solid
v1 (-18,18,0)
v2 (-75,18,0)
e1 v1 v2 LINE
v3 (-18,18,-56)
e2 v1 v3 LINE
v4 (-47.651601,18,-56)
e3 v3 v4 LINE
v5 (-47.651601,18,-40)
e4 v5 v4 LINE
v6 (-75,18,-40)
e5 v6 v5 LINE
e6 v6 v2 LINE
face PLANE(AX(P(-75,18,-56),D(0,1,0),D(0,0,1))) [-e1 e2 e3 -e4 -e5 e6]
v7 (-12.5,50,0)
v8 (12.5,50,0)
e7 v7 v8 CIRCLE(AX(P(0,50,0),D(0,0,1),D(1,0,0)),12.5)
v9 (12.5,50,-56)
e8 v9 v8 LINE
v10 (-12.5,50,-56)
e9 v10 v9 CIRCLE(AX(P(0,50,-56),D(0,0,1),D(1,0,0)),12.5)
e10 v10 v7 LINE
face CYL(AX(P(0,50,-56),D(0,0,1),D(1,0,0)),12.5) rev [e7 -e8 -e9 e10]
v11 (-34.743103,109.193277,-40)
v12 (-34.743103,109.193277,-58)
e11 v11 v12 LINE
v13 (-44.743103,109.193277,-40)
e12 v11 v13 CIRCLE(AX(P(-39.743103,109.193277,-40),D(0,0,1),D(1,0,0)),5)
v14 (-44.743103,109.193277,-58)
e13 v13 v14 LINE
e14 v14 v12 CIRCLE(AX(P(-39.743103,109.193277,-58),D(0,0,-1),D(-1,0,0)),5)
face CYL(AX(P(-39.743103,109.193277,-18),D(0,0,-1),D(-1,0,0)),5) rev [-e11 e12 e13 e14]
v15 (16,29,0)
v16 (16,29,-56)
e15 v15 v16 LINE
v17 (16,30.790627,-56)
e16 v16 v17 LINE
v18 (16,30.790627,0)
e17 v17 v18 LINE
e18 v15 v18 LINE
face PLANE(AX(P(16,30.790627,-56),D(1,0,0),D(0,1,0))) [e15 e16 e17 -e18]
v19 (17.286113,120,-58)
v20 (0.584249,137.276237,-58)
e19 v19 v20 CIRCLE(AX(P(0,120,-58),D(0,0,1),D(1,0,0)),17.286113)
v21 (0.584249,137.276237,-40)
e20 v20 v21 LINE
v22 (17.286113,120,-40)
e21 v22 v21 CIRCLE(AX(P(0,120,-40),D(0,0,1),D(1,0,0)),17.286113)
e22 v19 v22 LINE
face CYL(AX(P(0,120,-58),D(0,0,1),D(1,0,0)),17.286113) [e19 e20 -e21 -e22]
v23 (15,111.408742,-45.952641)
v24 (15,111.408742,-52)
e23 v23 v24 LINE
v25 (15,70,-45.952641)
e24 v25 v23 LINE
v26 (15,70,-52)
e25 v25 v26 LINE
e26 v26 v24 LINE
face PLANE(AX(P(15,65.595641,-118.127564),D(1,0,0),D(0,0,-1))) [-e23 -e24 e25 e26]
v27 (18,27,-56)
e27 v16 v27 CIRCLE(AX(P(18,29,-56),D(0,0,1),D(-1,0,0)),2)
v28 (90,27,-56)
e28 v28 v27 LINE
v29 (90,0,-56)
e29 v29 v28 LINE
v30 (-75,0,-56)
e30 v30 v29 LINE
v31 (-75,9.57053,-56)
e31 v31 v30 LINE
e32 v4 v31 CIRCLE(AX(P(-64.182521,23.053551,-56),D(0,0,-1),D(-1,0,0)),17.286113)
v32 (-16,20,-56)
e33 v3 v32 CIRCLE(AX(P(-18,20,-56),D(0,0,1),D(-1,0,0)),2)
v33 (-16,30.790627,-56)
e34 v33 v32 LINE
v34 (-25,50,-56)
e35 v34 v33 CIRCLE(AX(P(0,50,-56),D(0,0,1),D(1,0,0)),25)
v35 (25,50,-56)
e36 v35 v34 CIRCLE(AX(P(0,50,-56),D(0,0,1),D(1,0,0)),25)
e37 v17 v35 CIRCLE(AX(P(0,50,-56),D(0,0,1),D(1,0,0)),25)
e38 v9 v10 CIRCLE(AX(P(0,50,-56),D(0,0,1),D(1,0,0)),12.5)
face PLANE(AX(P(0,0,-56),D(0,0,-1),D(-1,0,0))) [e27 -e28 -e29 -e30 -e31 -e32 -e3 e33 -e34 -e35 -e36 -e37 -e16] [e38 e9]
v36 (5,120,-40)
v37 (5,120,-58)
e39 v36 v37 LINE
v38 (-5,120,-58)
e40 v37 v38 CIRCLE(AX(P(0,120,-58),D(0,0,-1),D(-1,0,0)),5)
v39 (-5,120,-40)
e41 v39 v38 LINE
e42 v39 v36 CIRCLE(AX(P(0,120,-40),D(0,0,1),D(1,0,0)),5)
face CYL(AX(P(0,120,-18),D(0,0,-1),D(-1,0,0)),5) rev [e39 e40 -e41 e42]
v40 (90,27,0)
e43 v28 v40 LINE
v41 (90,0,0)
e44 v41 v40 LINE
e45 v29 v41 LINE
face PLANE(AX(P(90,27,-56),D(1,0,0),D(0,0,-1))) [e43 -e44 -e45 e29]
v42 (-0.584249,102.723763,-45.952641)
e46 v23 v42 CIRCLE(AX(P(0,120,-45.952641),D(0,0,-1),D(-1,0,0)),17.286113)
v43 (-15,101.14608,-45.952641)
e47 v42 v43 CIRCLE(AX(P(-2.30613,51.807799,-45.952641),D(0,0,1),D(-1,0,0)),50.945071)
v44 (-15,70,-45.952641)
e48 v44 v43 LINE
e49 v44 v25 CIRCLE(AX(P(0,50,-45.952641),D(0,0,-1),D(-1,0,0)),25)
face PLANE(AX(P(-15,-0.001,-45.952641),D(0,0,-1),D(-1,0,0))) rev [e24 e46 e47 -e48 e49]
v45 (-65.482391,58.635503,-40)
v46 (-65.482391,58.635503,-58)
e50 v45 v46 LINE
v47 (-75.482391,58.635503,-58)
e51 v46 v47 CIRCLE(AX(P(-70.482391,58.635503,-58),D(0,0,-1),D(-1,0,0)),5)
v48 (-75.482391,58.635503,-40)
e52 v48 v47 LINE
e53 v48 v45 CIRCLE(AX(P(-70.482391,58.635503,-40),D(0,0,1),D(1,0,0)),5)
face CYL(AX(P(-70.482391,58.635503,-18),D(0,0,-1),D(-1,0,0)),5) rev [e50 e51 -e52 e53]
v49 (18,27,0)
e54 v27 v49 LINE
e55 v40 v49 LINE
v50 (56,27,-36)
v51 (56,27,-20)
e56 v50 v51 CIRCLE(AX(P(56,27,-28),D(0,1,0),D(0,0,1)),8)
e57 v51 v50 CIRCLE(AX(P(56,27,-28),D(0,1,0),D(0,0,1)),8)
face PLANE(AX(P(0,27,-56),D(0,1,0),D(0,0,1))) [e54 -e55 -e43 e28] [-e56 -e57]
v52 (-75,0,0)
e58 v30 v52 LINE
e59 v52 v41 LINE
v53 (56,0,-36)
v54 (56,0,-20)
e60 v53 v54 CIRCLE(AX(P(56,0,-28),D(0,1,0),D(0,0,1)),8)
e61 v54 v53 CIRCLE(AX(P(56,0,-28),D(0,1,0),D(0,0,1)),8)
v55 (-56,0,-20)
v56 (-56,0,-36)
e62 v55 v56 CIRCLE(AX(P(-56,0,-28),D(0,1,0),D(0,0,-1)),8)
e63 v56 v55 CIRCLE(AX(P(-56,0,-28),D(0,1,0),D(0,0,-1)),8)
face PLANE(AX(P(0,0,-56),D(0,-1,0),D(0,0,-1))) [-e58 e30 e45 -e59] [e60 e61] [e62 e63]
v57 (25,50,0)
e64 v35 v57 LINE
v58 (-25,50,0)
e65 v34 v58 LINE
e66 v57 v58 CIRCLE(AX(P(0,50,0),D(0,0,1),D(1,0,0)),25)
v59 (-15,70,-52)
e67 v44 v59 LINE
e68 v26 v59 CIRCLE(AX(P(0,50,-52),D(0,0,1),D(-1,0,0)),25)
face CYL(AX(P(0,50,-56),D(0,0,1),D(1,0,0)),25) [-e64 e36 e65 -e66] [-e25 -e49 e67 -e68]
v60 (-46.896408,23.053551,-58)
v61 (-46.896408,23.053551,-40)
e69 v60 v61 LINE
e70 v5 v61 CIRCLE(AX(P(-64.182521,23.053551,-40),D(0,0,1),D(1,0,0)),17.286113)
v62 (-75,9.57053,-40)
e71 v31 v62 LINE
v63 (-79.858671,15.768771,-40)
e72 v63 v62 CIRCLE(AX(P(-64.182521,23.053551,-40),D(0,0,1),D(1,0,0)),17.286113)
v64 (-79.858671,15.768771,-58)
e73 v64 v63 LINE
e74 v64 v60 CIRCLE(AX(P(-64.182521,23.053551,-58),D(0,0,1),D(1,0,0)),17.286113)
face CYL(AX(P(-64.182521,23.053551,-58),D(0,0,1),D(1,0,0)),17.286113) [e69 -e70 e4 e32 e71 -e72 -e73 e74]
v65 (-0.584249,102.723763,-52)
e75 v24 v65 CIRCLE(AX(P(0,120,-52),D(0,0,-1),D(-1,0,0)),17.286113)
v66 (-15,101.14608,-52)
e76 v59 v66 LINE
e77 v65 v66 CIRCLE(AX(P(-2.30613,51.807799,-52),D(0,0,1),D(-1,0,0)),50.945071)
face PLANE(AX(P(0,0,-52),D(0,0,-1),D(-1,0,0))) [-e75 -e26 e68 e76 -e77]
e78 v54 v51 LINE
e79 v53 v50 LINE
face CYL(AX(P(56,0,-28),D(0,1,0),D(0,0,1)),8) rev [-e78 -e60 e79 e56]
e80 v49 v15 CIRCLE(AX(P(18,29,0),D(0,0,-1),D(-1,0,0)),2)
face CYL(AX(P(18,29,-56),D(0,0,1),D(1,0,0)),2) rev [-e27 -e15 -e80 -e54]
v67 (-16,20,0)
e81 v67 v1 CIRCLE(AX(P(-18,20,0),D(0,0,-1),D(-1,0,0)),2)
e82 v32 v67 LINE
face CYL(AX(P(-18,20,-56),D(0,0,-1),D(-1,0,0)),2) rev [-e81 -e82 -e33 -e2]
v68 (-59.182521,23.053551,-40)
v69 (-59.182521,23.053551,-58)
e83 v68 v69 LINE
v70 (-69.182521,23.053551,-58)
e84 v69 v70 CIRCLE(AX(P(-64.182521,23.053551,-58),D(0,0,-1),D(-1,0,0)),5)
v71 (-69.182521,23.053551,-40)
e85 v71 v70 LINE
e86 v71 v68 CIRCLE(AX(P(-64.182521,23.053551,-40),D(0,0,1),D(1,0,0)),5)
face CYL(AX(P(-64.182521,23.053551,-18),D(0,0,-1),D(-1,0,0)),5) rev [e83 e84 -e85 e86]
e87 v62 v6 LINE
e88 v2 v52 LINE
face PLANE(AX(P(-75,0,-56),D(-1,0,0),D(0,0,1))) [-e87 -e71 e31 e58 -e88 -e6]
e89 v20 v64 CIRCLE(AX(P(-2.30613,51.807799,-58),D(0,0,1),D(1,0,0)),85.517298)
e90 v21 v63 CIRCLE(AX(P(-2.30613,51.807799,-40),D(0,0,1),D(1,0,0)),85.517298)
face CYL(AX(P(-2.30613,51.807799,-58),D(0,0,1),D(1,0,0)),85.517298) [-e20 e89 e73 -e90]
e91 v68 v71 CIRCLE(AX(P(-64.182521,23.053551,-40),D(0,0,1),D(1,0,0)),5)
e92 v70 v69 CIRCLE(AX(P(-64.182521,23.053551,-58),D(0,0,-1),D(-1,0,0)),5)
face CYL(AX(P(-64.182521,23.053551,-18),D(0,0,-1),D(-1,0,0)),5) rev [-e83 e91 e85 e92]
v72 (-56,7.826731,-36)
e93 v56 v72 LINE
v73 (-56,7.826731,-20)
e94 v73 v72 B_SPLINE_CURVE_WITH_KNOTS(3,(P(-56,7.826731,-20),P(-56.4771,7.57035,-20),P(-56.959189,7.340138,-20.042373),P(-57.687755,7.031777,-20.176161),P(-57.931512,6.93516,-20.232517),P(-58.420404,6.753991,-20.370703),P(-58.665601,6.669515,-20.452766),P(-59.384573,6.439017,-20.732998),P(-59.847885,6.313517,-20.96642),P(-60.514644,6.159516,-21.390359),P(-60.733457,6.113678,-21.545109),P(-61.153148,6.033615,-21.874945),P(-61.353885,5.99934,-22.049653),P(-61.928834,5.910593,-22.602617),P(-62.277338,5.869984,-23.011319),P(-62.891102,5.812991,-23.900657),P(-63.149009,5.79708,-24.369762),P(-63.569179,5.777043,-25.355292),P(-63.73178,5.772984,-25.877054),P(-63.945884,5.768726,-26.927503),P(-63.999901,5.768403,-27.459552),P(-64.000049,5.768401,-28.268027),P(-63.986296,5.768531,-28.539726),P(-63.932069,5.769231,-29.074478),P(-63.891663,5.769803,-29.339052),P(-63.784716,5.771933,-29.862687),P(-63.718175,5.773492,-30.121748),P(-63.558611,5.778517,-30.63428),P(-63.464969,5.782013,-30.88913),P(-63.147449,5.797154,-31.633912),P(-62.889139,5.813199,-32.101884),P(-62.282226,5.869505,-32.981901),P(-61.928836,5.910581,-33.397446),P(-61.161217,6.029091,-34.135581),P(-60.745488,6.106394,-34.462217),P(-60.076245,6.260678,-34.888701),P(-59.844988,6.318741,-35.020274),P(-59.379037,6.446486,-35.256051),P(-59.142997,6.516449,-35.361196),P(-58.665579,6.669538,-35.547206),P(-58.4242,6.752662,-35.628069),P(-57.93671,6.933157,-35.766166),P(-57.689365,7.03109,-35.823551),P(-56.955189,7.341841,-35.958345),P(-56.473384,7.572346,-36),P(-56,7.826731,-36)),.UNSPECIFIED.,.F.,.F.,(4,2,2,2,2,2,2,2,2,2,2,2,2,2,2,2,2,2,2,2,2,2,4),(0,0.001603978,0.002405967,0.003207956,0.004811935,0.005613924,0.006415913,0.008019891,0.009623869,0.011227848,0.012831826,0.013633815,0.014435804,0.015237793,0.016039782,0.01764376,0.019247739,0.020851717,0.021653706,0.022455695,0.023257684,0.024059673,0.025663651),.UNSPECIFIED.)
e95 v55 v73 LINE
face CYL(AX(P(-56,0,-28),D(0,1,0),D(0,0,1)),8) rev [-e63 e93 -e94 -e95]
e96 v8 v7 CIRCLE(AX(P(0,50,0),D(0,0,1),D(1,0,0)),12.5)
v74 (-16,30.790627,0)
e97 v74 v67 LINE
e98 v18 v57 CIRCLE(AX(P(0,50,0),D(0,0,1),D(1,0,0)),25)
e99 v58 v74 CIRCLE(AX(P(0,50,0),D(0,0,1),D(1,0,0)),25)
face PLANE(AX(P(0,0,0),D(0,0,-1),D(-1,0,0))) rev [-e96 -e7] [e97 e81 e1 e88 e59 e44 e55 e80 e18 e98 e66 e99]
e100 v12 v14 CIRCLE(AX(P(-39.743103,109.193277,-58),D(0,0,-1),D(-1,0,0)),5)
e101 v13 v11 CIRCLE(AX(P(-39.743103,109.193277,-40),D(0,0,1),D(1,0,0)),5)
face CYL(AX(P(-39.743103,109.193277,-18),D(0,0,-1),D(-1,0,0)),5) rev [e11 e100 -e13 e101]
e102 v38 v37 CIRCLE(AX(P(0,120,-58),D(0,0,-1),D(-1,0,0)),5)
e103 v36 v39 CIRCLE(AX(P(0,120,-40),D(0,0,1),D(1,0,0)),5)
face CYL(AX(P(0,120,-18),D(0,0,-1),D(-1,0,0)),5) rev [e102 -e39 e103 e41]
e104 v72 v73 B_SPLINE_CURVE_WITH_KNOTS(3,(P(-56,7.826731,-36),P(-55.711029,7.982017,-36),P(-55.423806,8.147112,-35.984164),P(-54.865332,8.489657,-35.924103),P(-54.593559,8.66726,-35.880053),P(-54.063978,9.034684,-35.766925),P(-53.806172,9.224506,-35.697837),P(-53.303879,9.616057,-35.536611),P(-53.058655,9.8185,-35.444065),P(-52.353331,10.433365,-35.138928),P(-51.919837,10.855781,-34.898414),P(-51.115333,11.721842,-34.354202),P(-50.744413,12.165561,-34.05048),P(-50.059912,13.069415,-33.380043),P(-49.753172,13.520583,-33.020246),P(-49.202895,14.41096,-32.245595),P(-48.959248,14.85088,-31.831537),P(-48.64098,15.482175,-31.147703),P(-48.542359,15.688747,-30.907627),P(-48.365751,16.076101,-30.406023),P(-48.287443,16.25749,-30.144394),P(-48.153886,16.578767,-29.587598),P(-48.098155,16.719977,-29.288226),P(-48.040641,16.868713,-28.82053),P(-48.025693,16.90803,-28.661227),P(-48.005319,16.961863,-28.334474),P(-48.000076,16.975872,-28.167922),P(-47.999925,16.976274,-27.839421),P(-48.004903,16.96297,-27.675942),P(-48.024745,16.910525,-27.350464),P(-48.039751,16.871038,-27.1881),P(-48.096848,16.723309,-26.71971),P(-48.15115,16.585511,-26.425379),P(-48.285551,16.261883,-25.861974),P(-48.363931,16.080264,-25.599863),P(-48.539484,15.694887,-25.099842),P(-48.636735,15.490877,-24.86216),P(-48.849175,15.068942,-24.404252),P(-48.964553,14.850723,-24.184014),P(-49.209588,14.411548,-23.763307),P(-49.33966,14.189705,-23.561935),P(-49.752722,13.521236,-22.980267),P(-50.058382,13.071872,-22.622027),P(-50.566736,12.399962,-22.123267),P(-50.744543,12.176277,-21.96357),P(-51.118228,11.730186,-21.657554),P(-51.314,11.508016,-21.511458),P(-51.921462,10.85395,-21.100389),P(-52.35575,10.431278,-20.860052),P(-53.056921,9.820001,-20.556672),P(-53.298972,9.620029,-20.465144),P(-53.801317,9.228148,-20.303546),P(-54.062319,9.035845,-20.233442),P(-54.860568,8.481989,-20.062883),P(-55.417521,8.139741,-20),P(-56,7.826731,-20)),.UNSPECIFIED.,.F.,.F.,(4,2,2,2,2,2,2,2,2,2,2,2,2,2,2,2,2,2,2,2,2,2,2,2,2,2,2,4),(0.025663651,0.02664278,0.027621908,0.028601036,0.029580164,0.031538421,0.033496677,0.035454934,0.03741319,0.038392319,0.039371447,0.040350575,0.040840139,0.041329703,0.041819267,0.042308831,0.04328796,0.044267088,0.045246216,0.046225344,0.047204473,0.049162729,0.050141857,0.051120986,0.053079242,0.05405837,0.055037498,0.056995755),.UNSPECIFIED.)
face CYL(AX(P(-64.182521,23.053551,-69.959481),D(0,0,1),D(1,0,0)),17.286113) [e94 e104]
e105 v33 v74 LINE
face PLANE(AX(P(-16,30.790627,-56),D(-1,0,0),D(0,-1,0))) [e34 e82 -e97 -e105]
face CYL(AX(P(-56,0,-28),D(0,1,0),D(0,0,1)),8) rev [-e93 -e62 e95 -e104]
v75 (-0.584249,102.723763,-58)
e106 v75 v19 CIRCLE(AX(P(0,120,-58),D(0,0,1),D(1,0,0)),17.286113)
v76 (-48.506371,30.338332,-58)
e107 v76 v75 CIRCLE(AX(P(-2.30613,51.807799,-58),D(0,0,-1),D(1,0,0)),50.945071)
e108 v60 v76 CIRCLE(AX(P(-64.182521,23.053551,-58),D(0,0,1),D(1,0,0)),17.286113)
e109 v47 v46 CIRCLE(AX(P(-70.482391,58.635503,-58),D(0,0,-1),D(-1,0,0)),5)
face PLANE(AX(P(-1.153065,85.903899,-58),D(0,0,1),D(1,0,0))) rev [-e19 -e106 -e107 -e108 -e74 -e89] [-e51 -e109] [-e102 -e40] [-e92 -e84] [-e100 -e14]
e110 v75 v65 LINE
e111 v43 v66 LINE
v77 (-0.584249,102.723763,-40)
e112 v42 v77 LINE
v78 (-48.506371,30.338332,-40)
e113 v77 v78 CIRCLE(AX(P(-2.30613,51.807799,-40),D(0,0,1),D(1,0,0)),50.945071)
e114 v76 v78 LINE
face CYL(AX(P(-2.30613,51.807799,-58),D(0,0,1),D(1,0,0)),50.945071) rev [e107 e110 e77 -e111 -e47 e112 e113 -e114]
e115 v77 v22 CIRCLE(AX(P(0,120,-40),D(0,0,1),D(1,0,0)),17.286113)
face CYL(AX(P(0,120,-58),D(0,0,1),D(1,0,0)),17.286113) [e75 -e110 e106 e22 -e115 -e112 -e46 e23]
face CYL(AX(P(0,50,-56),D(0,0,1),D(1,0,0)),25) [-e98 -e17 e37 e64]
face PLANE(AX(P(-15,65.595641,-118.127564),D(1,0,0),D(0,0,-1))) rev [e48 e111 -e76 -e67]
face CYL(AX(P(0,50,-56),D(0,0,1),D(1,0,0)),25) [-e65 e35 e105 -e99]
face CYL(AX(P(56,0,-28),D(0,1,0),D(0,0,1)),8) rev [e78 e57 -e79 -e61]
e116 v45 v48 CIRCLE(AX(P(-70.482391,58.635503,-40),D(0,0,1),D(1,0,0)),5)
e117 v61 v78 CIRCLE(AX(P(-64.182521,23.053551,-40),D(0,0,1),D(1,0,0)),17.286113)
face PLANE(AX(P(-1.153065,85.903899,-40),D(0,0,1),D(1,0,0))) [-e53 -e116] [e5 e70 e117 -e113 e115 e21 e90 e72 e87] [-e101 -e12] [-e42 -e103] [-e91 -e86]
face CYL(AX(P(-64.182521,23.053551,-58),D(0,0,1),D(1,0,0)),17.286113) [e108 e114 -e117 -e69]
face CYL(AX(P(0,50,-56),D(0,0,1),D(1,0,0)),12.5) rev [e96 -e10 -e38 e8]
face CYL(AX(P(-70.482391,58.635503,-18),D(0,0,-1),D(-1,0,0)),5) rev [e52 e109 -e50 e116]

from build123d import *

# Parameters (mm, degrees)
BASE_PLATE_DEPTH            = 56
HUB_BOSS_SKETCH_R           = 12.5
HUB_BOSS_DEPTH              = 56
HUB_FILLET_R2_R             = 2
WEB_SKETCH_W                = 30
WEB_SKETCH_H                = 54.40435867
WEB_4MM_DEPTH               = 52
HUB_BORE_REACH              = 162.112
HUB_BORE_END_RADIUS         = 25
HUB_BORE_SKETCH_W           = 30
HUB_BORE_SKETCH_H           = 45.952641166
FLANGE_PLATE_DEPTH          = 58
FLANGE_SLOT_CUT_DEPTH       = 40
FLANGE_BOLT_HOLES_SKETCH_R  = 5
FLANGE_BOLT_HOLES_DEPTH     = 40
BASE_MOUNTING_HOLE_SKETCH_R = 8
BASE_MOUNTING_HOLE_DEPTH    = 154.738826956
FLANGE_CLOSING_BOSS_DEPTH   = 40


with BuildPart() as part:
    # Base Plate Sketch → Base Plate (new body)
    with BuildSketch(Plane.XY):
        Polygon((0, 0), (-75, 0), (-75, 18), (0, 18), (0, 27), (90, 27), (90, 0), align=None)
    extrude(amount=-BASE_PLATE_DEPTH)

    # Hub Boss Sketch → Hub Boss (add)
    with BuildSketch(Plane.XY):
        with BuildLine():
            Line((-16, 30.790627288), (-16, 18))
            Line((-16, 18), (16, 18))
            Line((16, 18), (16, 30.790627288))
            ThreePointArc((16, 30.790627288), (0, 75), (-16, 30.790627288))
        make_face()
        with Locations((0, 50)):
            Circle(HUB_BOSS_SKETCH_R, mode=Mode.SUBTRACT)
    extrude(amount=-HUB_BOSS_DEPTH)

    # Hub Fillet R2
    hub_fillet_r2_edges = [part.edges().sort_by_distance(p)[0] for p in [
        (16, 27, -28),
        (-16, 18, -28),
    ]]
    fillet(hub_fillet_r2_edges, radius=HUB_FILLET_R2_R)

    # Web Sketch → Web 4mm (add)
    with BuildSketch(Plane.XY):
        with Locations((0, 92.797820665)):
            Rectangle(WEB_SKETCH_W, WEB_SKETCH_H)
    extrude(amount=-WEB_4MM_DEPTH)

    # Hub Bore: up to this cylinder (the profile starts outside it)
    hub_bore_end = Plane(origin=(0, 50, -22.976321), z_dir=(0, 0, 1)) * Cylinder(HUB_BORE_END_RADIUS, 375.224, mode=Mode.PRIVATE)
    # Hub Bore Sketch → Hub Bore (cut, up to the surface)
    with BuildSketch(Plane(origin=(0, 120, 0), x_dir=(1, 0, 0), z_dir=(0, 1, 0)), mode=Mode.PRIVATE) as hub_bore_sk1:
        with Locations((0, 22.976320583)):
            Rectangle(HUB_BORE_SKETCH_W, HUB_BORE_SKETCH_H)
    hub_bore_tool1 = extrude(hub_bore_sk1.sketch, amount=-HUB_BORE_REACH, mode=Mode.PRIVATE) - hub_bore_end
    add(hub_bore_tool1.solids().sort_by_distance((0, 120, -22.976321))[0], mode=Mode.SUBTRACT)

    # Flange Profile Sketch → Flange Plate (add)
    with BuildSketch(Plane.XY):
        with BuildLine():
            ThreePointArc((0.584249397, 137.276236883), (-73.612691272, 99.015664074), (-79.858671486, 15.768771234))
            ThreePointArc((-79.858671486, 15.768771234), (-56.897741093, 7.377401147), (-48.506371007, 30.33833154))
            ThreePointArc((-48.506371007, 30.33833154), (-44.785464057, 79.930858496), (-0.584249397, 102.723763117))
            ThreePointArc((-0.584249397, 102.723763117), (17.276236883, 119.415750603), (0.584249397, 137.276236883))
        make_face()
    extrude(amount=-FLANGE_PLATE_DEPTH)

    # Sketch7_2 → Flange Slot Cut (cut)
    with BuildSketch(Plane.XY):
        with BuildLine():
            ThreePointArc((0.584249397, 137.276236883), (-73.612691272, 99.015664074), (-79.858671486, 15.768771234))
            ThreePointArc((-79.858671486, 15.768771234), (-56.897741093, 7.377401147), (-48.506371007, 30.33833154))
            ThreePointArc((-48.506371007, 30.33833154), (-44.785464057, 79.930858496), (-0.584249397, 102.723763117))
            ThreePointArc((-0.584249397, 102.723763117), (17.276236883, 119.415750603), (0.584249397, 137.276236883))
        make_face()
    extrude(amount=-FLANGE_SLOT_CUT_DEPTH, mode=Mode.SUBTRACT)

    # Flange Bolt Holes Sketch → Flange Bolt Holes (cut)
    with BuildSketch(Plane(origin=(0, 0, -58), x_dir=(-1, 0, 0), z_dir=(0, 0, -1))):
        with Locations((0, 120)):
            Circle(FLANGE_BOLT_HOLES_SKETCH_R)
        with Locations((39.743102788, 109.193277489)):
            Circle(FLANGE_BOLT_HOLES_SKETCH_R)
        with Locations((70.482390924, 58.635502651)):
            Circle(FLANGE_BOLT_HOLES_SKETCH_R)
        with Locations((64.182521246, 23.053551387)):
            Circle(FLANGE_BOLT_HOLES_SKETCH_R)
    extrude(amount=-FLANGE_BOLT_HOLES_DEPTH, mode=Mode.SUBTRACT)

    # Base Mounting Hole Sketch → Base Mounting Hole (cut, through all)
    with BuildSketch(Plane(origin=(0, 27, 0), x_dir=(1, 0, 0), z_dir=(0, 1, 0))):
        with Locations(Location((56, 28, 0), (0, 0, 270))):
            Circle(BASE_MOUNTING_HOLE_SKETCH_R)
        with Locations(Location((-56, 28, 0), (0, 0, 270))):
            Circle(BASE_MOUNTING_HOLE_SKETCH_R)
    extrude(amount=-BASE_MOUNTING_HOLE_DEPTH, mode=Mode.SUBTRACT)

    # Flange Closing Boss Sketch → Flange Closing Boss (add)
    with BuildSketch(Plane.XY):
        with BuildLine():
            Line((-47.651600927, 18), (-75, 18))
            Line((-75, 18), (-75, 9.570530152))
            ThreePointArc((-75, 9.570530152), (-59.090876707, 6.534324283), (-47.651600927, 18))
        make_face()
    extrude(amount=-FLANGE_CLOSING_BOSS_DEPTH)


solid = part.part
